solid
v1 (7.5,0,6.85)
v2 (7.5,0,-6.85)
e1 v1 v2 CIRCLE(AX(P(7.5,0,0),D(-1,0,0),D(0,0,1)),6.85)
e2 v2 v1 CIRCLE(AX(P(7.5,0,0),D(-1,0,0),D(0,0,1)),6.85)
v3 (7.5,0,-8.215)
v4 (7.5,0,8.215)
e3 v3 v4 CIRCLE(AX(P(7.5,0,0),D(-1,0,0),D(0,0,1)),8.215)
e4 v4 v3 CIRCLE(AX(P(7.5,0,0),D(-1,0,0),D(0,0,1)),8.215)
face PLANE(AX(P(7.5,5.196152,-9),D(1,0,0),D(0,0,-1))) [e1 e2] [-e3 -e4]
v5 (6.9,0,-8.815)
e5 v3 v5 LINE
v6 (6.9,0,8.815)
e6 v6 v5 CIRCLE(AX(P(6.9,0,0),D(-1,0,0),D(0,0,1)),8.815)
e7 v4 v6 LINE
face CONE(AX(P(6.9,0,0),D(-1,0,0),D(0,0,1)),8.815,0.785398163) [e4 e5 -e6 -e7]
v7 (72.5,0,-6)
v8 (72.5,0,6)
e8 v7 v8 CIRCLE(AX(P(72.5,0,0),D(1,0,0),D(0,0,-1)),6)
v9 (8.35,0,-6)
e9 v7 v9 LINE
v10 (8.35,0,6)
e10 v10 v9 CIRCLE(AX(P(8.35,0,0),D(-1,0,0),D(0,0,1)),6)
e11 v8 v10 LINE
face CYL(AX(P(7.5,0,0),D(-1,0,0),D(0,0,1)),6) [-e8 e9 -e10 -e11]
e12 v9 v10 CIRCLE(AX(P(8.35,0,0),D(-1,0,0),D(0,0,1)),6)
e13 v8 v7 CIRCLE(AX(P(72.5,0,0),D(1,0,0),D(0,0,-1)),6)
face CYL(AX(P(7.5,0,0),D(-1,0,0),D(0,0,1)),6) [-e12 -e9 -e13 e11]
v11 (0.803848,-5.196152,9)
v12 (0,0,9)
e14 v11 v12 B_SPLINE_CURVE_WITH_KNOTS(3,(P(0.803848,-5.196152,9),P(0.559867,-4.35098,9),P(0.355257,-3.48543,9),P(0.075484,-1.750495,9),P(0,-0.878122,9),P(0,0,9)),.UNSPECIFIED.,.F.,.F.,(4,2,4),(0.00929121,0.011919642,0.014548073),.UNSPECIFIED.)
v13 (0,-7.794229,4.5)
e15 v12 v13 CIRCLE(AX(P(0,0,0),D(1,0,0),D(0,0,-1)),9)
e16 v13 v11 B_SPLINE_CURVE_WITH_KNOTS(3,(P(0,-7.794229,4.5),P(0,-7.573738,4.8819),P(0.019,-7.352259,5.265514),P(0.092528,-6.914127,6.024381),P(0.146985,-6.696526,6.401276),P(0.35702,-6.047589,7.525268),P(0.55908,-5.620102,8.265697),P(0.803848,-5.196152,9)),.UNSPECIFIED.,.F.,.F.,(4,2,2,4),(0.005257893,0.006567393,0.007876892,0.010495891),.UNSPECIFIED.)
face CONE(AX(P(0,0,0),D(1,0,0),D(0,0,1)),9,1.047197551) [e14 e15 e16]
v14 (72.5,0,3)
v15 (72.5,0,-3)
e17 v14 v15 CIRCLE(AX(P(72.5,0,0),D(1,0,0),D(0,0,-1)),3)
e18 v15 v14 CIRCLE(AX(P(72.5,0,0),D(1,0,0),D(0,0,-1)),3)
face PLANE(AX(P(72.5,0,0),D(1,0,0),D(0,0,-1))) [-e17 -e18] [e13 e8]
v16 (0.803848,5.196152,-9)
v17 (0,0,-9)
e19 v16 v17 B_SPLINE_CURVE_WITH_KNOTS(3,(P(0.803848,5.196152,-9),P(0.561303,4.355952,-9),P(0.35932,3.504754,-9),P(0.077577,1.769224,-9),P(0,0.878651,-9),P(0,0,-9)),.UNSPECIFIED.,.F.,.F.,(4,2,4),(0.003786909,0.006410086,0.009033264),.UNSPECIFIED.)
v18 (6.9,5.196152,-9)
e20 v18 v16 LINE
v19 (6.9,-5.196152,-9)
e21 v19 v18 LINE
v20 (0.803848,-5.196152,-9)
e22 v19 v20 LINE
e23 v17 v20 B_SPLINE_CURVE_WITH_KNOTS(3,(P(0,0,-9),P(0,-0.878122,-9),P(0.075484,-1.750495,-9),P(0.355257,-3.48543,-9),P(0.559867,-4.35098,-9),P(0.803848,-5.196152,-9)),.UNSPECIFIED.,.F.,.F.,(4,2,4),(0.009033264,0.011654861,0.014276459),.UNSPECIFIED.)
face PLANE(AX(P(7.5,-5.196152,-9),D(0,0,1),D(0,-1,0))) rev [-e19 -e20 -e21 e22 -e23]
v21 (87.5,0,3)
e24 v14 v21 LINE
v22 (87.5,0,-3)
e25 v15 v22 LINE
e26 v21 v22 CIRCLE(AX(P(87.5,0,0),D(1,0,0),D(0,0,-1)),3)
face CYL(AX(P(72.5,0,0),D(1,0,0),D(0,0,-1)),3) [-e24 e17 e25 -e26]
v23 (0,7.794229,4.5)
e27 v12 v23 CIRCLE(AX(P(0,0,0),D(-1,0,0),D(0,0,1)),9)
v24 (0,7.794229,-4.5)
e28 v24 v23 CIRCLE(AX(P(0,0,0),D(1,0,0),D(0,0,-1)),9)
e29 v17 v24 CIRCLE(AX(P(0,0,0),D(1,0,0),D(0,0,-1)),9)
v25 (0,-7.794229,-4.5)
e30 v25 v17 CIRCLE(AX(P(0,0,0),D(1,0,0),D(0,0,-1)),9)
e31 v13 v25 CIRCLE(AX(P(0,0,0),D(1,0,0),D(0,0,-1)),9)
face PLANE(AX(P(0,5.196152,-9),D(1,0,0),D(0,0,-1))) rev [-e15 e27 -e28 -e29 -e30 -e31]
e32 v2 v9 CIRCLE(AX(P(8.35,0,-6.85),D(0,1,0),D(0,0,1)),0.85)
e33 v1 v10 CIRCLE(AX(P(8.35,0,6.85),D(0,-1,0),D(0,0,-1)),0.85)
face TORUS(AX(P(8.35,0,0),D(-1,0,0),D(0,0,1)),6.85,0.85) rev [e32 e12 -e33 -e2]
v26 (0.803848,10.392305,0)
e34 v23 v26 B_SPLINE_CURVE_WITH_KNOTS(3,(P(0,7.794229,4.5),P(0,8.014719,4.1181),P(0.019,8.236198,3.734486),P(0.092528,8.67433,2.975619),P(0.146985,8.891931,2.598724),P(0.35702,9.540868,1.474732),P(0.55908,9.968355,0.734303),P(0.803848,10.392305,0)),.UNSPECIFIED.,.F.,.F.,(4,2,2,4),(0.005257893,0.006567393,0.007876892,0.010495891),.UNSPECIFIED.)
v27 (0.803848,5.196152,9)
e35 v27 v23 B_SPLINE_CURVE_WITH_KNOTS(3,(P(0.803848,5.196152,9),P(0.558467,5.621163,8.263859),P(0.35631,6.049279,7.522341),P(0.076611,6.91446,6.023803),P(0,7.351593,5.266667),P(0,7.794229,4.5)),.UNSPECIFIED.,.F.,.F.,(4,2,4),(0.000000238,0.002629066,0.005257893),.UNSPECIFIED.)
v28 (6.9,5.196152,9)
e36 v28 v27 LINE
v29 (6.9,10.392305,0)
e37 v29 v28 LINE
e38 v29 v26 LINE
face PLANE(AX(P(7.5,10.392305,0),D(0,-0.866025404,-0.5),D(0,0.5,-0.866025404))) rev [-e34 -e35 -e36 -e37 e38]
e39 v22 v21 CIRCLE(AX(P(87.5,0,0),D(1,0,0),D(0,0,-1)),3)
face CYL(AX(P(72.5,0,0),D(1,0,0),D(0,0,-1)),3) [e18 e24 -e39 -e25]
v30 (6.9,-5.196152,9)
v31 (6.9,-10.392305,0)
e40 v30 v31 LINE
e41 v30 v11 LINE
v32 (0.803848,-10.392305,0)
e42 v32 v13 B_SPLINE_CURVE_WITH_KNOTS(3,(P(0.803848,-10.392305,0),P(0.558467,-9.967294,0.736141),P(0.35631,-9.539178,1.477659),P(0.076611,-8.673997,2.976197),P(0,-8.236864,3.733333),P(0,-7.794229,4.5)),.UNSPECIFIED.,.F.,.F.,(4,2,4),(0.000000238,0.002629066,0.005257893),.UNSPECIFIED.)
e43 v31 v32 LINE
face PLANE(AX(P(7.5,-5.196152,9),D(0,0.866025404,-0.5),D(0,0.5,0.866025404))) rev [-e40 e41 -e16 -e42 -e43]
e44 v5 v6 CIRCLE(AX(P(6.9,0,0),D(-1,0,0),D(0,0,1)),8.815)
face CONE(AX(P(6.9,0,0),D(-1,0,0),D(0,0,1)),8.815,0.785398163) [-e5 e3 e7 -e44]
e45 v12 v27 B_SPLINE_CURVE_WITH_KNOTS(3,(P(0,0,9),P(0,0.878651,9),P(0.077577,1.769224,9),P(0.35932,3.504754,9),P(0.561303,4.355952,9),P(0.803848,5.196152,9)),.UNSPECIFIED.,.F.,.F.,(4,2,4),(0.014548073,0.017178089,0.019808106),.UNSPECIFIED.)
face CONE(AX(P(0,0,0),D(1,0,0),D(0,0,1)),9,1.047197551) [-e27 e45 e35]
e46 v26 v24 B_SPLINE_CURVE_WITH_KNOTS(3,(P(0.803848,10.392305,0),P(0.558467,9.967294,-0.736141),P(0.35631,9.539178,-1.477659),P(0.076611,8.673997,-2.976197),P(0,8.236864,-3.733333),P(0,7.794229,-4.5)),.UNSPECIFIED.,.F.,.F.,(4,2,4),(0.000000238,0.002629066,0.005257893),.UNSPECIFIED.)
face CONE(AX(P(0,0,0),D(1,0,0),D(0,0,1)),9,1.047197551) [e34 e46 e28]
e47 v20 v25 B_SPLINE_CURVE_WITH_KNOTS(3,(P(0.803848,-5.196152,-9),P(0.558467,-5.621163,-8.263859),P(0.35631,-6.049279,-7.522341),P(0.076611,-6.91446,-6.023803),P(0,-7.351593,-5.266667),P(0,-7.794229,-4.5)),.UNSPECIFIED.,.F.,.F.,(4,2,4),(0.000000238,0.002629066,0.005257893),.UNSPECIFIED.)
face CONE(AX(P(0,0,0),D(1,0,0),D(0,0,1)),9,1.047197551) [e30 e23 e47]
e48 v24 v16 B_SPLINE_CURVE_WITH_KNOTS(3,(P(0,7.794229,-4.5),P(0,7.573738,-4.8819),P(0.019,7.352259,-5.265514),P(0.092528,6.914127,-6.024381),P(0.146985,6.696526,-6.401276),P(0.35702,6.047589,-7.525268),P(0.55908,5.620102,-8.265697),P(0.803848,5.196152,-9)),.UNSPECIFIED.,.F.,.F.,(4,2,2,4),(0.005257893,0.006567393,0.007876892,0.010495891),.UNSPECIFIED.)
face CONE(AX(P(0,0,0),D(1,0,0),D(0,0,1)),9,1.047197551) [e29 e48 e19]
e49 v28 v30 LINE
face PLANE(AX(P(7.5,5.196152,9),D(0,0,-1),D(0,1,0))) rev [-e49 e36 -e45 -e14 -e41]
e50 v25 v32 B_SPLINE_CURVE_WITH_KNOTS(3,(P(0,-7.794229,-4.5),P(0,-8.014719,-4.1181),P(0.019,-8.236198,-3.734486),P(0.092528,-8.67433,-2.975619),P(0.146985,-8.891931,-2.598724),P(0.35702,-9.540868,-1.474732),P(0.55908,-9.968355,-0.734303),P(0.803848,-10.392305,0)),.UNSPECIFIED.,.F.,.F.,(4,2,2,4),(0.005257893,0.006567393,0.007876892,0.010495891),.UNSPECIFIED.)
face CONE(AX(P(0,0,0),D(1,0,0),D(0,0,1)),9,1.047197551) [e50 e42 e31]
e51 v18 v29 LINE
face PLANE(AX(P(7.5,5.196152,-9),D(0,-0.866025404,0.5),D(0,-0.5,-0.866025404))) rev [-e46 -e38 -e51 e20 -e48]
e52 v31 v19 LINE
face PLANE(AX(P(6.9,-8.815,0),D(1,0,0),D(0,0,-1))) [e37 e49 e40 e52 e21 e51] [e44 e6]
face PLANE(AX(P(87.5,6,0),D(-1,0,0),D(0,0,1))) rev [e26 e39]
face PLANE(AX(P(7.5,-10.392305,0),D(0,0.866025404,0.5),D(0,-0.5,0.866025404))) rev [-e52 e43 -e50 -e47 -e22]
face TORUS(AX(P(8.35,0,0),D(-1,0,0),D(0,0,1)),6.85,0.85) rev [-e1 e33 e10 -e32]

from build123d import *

# Parameters (mm, degrees)
BOSS_EXTRUDE1_DEPTH = 7.5
SKETCH4_R           = 20.03
SKETCH4_R_2         = 9
CUT_EXTRUDE1_DEPTH  = 0.9375
CUT_EXTRUDE1_DRAFT  = -60
CHAMFER2_SIZE       = 0.666666667
SKETCH9_R           = 8.815
SKETCH9_R_2         = 3
CUT_EXTRUDE2_DEPTH  = 15


with BuildPart() as part:
    # Sketch3 → Boss-Extrude1 (new body)
    with BuildSketch(Plane(origin=(0, 0, 0), x_dir=(0, 0, -1), z_dir=(1, 0, 0))):
        Polygon((9, 5.196152423), (0, 10.392304845), (-9, 5.196152423), (-9, -5.196152423), (0, -10.392304845), (9, -5.196152423), align=None)
    extrude(amount=BOSS_EXTRUDE1_DEPTH)


with BuildPart() as cut_extrude1_tool:
    # Sketch4 → Cut-Extrude1 (with draft: the straight prism first)
    with BuildSketch(Plane.ZY):
        Circle(SKETCH4_R)
        Circle(SKETCH4_R_2, mode=Mode.SUBTRACT)
    extrude(amount=-CUT_EXTRUDE1_DEPTH)
    # Cut-Extrude1: the draft: its side faces are tilted about the plane it starts from
    cut_extrude1_sides = [cut_extrude1_tool.faces().sort_by_distance(p)[0] for p in [
        (0.46875, 0, -20.03),
        (0.46875, 0, -9),
    ]]
    draft(cut_extrude1_sides, Plane.ZY, CUT_EXTRUDE1_DRAFT)


with BuildPart() as part_1:
    add(part.part)

    # Cut-Extrude1: cut by cut_extrude1_tool
    add(cut_extrude1_tool.part, mode=Mode.SUBTRACT)

    # Sketch5 → Revolve1 (revolve)
    with BuildSketch(Plane.XY, mode=Mode.PRIVATE) as revolve1_sk:
        with BuildLine():
            Line((8.35, 6), (87.5, 6))
            Line((87.5, 6), (87.5, 0))
            Line((87.5, 0), (7.5, 0))
            Line((7.5, 0), (7.5, 6.85))
            ThreePointArc((7.5, 6.85), (7.748959236, 6.248959236), (8.35, 6))
        make_face()
    revolve(revolve1_sk.sketch.rotate(Axis((7.5, 0, 0), (1, 0, 0)), 90), axis=Axis((7.5, 0, 0), (1, 0, 0)))

    # Chamfer2
    chamfer2_edges = [part_1.edges().sort_by_distance(p)[0] for p in [
        (87.5, 0, -6),
    ]]
    chamfer(chamfer2_edges, length=CHAMFER2_SIZE)

    # Sketch7 → Cut-Revolve1 (revolve, cut)
    with BuildSketch(Plane.XY, mode=Mode.PRIVATE) as cut_revolve1_sk:
        Polygon((7.5, 8.215), (6.9, 8.815), (6.9, 20.03), (7.5, 20.03), align=None)
    revolve(cut_revolve1_sk.sketch.rotate(Axis((0, 0, 0), (1, 0, 0)), 90), axis=Axis((0, 0, 0), (1, 0, 0)), mode=Mode.SUBTRACT)

    # Sketch9 → Cut-Extrude2 (cut)
    with BuildSketch(Plane(origin=(87.5, 0, 0), x_dir=(0, 0, -1), z_dir=(1, 0, 0))):
        Circle(SKETCH9_R)
        Circle(SKETCH9_R_2, mode=Mode.SUBTRACT)
    extrude(amount=-CUT_EXTRUDE2_DEPTH, mode=Mode.SUBTRACT)


solid = part_1.part
